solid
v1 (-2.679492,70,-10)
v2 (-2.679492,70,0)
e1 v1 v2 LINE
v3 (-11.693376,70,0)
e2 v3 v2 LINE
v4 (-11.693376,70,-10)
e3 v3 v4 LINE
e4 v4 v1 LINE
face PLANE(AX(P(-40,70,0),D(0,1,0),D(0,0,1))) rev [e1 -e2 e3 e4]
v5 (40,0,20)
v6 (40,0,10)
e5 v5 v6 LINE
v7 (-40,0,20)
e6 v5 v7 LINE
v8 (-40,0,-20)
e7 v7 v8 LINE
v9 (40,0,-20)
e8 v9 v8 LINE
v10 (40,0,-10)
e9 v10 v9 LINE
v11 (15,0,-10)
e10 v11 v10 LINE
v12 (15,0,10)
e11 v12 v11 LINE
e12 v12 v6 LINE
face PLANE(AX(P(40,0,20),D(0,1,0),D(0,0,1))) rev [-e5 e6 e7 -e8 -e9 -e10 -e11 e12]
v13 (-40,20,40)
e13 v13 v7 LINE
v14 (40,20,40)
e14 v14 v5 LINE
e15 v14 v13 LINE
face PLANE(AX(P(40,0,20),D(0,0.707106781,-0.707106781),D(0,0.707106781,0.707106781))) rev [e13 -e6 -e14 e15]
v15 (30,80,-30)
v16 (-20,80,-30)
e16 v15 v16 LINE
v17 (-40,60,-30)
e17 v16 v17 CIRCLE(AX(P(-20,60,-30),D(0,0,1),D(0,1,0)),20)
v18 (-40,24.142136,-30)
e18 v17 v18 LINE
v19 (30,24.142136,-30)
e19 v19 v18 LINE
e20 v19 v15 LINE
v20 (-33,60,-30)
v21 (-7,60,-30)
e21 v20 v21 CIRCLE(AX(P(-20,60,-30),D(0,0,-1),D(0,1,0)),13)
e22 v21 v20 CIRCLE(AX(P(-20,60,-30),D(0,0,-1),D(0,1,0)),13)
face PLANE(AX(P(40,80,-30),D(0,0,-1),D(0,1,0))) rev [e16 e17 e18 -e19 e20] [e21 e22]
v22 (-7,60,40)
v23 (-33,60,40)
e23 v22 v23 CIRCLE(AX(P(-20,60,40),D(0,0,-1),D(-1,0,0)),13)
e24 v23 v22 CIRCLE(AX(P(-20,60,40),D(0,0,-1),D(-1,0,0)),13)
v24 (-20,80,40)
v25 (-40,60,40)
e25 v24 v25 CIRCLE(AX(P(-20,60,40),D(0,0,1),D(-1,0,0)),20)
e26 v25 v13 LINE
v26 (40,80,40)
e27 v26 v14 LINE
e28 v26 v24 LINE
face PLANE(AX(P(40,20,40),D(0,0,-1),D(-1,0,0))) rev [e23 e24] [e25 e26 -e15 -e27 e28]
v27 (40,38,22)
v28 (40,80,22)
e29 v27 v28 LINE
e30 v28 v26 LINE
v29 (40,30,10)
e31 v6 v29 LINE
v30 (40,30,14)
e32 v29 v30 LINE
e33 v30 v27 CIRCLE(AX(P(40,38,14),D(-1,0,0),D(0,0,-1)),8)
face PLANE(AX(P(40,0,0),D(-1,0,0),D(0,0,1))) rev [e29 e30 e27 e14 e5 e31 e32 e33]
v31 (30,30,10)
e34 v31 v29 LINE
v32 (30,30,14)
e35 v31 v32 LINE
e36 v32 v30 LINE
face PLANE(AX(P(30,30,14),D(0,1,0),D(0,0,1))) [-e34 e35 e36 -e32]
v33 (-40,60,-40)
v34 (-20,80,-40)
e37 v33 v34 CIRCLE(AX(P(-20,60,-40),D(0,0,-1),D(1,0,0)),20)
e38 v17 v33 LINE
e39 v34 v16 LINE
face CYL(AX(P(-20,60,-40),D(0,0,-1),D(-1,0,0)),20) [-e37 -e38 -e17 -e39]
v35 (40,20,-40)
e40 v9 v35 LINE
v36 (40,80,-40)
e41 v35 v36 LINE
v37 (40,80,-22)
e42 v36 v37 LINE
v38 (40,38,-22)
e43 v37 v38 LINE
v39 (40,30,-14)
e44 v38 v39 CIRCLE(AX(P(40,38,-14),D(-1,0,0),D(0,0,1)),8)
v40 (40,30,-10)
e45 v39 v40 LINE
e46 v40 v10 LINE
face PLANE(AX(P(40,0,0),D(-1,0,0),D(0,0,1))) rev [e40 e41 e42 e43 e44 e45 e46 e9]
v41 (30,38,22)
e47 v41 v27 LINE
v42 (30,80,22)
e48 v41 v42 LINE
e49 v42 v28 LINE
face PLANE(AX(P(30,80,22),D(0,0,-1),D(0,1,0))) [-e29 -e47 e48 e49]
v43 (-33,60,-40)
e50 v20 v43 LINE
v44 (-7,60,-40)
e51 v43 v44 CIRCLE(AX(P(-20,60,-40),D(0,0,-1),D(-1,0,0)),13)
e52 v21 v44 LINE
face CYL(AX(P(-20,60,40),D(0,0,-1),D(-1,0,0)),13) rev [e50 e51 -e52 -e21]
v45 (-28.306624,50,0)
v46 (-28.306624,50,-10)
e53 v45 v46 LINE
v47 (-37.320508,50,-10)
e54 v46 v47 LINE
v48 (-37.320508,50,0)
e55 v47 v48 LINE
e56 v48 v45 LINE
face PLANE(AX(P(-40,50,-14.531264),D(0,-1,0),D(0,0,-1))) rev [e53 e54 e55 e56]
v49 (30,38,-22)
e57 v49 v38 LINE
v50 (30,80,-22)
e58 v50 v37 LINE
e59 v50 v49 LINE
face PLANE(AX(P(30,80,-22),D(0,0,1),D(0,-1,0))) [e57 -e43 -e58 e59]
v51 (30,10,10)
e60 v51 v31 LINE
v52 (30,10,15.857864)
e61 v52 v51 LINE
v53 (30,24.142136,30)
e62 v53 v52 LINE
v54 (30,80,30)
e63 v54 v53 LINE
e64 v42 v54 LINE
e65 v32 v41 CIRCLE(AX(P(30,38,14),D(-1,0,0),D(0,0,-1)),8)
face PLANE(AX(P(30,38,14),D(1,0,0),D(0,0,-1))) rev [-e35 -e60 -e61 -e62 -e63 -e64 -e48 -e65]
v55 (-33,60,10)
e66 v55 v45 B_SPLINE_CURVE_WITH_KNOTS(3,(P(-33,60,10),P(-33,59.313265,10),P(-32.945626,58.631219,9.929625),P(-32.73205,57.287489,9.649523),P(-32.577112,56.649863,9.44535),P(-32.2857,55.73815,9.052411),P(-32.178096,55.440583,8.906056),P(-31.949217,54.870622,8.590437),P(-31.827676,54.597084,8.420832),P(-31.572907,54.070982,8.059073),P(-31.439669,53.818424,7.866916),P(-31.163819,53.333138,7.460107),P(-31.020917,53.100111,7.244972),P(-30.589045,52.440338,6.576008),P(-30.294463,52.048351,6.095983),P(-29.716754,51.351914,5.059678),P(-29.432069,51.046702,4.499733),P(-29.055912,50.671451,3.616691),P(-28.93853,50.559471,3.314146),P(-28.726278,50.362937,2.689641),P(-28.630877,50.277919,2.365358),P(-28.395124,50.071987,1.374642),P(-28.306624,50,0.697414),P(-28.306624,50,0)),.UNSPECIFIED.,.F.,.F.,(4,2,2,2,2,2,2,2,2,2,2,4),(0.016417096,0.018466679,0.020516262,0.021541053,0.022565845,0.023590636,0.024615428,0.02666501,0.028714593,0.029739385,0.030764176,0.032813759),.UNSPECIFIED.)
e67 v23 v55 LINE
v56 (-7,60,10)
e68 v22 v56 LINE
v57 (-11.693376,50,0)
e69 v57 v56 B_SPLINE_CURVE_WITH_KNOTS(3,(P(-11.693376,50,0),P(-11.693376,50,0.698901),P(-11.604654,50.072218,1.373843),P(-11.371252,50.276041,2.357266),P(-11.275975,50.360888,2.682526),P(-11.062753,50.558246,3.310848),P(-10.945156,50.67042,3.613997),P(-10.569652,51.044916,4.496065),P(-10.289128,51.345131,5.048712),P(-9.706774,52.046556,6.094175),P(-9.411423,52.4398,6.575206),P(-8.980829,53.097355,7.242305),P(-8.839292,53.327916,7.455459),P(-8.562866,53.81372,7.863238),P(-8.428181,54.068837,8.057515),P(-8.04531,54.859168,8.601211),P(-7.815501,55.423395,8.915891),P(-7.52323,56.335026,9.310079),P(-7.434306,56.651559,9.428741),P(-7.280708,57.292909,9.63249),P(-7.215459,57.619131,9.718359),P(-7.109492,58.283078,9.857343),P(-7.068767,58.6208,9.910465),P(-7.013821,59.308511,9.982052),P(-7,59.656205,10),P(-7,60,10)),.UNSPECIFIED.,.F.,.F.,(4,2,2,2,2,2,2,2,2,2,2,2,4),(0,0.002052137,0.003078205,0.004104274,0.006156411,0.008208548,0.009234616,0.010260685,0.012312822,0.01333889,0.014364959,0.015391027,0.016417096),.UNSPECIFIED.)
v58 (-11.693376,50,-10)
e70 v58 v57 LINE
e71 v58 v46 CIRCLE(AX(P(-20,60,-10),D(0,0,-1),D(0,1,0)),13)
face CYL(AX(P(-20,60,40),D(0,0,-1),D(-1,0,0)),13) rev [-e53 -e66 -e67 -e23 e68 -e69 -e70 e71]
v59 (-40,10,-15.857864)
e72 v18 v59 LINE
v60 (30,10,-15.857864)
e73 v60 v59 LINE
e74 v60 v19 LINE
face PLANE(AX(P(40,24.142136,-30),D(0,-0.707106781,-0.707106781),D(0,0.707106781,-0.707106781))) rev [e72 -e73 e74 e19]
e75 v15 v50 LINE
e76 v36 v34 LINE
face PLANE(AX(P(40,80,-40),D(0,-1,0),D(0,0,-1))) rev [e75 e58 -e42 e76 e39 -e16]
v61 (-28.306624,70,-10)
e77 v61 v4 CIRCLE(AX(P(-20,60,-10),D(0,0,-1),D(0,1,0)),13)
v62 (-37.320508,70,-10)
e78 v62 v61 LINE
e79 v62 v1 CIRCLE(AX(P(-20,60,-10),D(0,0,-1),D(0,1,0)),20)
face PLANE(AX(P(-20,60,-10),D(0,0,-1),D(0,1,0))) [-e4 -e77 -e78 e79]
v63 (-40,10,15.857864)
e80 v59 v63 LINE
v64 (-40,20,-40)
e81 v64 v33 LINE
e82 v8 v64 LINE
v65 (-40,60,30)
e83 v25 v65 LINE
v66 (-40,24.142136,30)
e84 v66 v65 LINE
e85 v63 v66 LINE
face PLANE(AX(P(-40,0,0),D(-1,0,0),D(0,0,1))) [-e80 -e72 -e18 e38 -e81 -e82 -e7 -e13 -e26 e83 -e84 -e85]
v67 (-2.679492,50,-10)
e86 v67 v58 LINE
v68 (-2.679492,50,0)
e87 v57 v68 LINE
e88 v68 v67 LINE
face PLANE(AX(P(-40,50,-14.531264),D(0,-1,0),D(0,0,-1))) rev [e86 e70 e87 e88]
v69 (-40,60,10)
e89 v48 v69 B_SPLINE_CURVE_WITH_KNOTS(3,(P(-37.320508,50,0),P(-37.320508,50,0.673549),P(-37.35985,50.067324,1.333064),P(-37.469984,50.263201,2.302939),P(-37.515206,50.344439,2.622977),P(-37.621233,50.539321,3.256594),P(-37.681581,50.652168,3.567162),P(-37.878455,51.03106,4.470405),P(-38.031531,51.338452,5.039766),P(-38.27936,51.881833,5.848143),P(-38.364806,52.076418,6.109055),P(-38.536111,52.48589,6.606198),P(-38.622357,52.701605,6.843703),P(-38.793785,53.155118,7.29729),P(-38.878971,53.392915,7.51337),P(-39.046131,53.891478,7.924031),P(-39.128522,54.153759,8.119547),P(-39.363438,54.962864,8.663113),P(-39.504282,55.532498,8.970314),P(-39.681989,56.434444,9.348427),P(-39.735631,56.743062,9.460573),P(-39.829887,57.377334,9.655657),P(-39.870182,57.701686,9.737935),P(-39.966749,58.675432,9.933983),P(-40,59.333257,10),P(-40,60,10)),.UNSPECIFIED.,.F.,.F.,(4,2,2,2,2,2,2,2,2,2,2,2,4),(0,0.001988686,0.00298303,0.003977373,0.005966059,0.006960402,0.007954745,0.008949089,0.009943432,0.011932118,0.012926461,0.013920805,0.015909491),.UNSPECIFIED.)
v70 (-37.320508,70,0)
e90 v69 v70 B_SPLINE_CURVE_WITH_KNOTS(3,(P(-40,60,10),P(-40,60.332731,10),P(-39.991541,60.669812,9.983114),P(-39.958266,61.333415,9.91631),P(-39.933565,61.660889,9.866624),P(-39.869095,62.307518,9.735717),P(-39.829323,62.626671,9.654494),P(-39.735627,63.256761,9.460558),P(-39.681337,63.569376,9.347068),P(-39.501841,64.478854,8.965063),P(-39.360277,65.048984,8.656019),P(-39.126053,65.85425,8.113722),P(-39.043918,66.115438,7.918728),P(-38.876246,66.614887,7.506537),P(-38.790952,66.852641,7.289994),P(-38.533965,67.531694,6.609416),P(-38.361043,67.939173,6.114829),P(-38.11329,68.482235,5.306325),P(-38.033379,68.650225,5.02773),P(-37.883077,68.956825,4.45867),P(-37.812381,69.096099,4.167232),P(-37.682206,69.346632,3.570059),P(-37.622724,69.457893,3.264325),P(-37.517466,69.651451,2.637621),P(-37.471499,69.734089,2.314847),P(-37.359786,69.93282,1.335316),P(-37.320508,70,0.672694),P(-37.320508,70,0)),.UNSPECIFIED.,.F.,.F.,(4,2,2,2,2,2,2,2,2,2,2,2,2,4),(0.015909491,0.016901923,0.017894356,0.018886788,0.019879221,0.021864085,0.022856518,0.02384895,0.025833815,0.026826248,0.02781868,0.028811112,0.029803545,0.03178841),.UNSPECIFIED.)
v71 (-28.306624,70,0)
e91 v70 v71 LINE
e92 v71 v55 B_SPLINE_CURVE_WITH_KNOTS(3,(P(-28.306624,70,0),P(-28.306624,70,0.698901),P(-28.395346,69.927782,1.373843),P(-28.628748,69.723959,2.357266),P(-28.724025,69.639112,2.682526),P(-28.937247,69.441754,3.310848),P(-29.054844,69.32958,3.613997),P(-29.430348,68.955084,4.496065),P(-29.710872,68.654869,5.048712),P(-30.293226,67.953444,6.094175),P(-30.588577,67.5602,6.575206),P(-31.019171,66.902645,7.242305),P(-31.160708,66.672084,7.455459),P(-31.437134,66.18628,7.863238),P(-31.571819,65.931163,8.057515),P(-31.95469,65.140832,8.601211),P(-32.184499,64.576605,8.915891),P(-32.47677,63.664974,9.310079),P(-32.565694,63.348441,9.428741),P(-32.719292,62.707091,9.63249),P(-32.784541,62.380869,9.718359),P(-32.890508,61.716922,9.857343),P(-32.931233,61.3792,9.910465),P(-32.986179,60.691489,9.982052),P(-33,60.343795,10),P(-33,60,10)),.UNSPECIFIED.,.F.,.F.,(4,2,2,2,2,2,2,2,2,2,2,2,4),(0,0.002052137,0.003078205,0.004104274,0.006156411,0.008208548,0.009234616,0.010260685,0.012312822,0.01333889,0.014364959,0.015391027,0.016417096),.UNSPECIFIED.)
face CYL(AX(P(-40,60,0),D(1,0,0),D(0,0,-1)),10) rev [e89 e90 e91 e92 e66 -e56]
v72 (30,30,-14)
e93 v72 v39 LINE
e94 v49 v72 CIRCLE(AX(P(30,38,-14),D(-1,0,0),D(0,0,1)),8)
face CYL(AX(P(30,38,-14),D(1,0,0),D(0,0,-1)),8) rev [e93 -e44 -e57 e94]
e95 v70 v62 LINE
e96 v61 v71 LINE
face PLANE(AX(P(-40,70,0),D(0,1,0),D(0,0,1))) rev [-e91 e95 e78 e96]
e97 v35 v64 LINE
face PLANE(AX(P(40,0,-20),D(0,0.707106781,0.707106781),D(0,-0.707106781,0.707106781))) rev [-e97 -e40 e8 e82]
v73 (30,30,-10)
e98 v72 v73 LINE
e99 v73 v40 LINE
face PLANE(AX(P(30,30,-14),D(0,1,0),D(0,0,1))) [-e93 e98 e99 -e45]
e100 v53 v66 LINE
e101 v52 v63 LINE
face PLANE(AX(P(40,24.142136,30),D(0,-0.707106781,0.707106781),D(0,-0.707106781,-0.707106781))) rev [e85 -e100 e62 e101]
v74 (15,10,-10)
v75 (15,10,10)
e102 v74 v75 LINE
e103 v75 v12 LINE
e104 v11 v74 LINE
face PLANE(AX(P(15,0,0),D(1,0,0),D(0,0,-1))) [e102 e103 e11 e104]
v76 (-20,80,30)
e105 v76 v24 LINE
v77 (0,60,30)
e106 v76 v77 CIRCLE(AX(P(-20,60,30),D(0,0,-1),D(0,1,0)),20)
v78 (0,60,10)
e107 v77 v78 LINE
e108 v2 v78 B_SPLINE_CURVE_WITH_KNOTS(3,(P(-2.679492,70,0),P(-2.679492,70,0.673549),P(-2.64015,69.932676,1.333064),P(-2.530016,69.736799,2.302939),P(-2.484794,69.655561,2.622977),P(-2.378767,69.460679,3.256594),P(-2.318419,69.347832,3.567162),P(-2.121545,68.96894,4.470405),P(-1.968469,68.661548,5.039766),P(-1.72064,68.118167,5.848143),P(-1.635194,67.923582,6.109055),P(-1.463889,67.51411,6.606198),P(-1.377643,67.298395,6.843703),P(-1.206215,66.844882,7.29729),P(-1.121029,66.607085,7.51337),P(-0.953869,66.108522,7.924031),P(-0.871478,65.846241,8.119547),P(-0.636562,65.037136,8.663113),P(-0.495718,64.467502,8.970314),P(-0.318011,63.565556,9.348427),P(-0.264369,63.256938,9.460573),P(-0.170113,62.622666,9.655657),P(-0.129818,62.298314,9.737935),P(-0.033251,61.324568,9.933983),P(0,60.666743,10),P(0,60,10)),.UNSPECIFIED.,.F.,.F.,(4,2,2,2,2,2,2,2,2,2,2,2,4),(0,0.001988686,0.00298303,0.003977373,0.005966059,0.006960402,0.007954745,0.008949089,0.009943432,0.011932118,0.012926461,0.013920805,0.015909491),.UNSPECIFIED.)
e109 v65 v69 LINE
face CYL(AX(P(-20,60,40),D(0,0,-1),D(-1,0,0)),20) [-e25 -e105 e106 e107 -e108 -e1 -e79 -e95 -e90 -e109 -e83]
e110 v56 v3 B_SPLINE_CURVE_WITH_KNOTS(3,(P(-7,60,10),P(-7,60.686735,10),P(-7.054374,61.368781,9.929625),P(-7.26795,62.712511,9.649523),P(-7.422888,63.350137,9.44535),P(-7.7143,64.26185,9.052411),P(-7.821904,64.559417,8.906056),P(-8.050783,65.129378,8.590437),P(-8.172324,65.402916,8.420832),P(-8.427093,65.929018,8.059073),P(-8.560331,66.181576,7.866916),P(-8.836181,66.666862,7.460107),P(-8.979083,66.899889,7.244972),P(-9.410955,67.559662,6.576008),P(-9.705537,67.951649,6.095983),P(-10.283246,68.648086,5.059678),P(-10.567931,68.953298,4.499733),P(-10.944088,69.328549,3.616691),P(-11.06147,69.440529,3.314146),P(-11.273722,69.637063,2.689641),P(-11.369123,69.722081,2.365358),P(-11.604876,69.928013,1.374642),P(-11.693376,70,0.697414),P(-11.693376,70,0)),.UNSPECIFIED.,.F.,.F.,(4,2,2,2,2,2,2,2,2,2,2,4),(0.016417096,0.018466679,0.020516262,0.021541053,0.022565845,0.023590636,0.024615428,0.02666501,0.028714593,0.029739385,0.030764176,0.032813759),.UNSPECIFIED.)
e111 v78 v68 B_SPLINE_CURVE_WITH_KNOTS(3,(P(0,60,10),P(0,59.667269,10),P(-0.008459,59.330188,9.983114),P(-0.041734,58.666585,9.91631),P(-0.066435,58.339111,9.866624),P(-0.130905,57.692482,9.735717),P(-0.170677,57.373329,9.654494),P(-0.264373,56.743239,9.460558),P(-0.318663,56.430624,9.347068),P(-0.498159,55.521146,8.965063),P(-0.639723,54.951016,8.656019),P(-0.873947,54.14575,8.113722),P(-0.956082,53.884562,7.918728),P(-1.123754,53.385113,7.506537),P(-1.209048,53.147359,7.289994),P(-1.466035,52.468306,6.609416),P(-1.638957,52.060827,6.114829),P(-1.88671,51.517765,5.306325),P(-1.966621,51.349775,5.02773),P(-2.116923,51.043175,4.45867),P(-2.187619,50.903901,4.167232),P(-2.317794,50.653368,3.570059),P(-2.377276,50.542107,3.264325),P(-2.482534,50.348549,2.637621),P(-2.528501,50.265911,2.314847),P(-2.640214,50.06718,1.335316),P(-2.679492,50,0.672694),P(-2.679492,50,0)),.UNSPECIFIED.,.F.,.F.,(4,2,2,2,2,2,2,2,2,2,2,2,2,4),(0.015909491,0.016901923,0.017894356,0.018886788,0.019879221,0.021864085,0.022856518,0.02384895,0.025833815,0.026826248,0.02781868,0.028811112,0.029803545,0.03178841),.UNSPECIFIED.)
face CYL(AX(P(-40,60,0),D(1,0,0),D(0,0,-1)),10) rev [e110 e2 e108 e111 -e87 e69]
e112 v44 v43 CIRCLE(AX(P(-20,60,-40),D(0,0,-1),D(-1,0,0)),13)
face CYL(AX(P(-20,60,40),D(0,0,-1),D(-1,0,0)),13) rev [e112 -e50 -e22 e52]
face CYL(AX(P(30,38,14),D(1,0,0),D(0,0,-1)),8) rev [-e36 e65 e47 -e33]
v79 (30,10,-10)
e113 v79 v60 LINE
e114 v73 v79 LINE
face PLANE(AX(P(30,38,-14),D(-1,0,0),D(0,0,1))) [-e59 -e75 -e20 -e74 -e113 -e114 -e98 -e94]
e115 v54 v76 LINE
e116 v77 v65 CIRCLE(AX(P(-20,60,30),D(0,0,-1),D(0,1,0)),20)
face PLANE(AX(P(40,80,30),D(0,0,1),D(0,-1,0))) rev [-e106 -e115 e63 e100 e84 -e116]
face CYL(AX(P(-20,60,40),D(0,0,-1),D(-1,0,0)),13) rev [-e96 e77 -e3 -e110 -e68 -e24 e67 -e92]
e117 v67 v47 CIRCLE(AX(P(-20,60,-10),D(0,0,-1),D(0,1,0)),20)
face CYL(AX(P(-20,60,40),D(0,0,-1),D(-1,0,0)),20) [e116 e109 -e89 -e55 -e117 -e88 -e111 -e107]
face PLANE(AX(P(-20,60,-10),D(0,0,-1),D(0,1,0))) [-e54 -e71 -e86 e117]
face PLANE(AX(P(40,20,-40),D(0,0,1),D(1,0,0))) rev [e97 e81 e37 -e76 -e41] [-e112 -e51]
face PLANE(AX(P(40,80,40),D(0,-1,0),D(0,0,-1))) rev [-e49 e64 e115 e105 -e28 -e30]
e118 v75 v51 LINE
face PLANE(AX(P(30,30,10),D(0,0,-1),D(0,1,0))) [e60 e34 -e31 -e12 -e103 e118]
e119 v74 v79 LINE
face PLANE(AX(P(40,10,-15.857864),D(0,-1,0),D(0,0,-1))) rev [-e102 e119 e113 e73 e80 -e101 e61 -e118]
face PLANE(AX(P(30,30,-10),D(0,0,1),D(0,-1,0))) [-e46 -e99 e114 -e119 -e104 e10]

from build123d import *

# Parameters (mm, degrees)
SADDLE_BODY_DEPTH     = 40
ARM_TOP_ROUNDS_R20_R  = 20
SIDE_BOSS_DEPTH       = 10
BOSS_POCKET_SKETCH_W  = 20
BOSS_POCKET_SKETCH_H  = 10
BOSS_POCKET_CUT_DEPTH = 25
JOURNAL_BOSS_SKETCH_R = 20
JOURNAL_BOSS_DEPTH    = 40
BASE_SLOT_20X60_DEPTH = 98.979589711
JOURNAL_BORE_SKETCH_R = 13
JOURNAL_BORE_26_DEPTH = 121.0000001


with BuildPart() as part:
    # Saddle Profile Sketch → Saddle Body (new, symmetric)
    with BuildSketch(Plane(origin=(0, 0, 0), x_dir=(0, 0, -1), z_dir=(1, 0, 0))):
        Polygon((-20, 0), (20, 0), (40, 20), (40, 80), (30, 80), (30, 24.142135624), (15.857864376, 10), (-15.857864376, 10), (-30, 24.142135624), (-30, 80), (-40, 80), (-40, 20), align=None)
    extrude(amount=SADDLE_BODY_DEPTH, both=True)

    # Arm Top Rounds R20
    arm_top_rounds_r20_edges = [part.edges().sort_by_distance(p)[0] for p in [
        (-40, 80, 35),
        (-40, 80, -35),
    ]]
    fillet(arm_top_rounds_r20_edges, radius=ARM_TOP_ROUNDS_R20_R)

    # Side Boss Sketch → Side Boss (add)
    with BuildSketch(Plane(origin=(40, 0, 0), x_dir=(0, 0, -1), z_dir=(1, 0, 0))):
        with BuildLine():
            Line((-30, 80), (-22, 80))
            Line((-22, 80), (-22, 38))
            ThreePointArc((-22, 38), (-19.656854249, 32.343145751), (-14, 30))
            Line((-14, 30), (-10, 30))
            Line((-10, 30), (-10, 10))
            Line((-10, 10), (-15.857864376, 10))
            Line((-15.857864376, 10), (-30, 24.142135624))
            Line((-30, 24.142135624), (-30, 80))
        make_face()
        with BuildLine():
            Line((10, 30), (10, 10))
            Line((10, 10), (15.857864376, 10))
            Line((15.857864376, 10), (30, 24.142135624))
            Line((30, 24.142135624), (30, 80))
            Line((30, 80), (22, 80))
            Line((22, 80), (22, 38))
            ThreePointArc((22, 38), (19.656854249, 32.343145751), (14, 30))
            Line((14, 30), (10, 30))
        make_face()
    extrude(amount=-SIDE_BOSS_DEPTH)

    # Boss Pocket Sketch → Boss Pocket Cut (cut)
    with BuildSketch(Plane(origin=(40, 0, 0), x_dir=(0, 0, -1), z_dir=(1, 0, 0))):
        with Locations((0, 5)):
            Rectangle(BOSS_POCKET_SKETCH_W, BOSS_POCKET_SKETCH_H)
    extrude(amount=-BOSS_POCKET_CUT_DEPTH, mode=Mode.SUBTRACT)

    # Journal Boss Sketch → Journal Boss (add)
    with BuildSketch(Plane(origin=(0, 0, 30), x_dir=(-1, 0, 0), z_dir=(0, 0, -1))):
        with Locations(Location((20, 60, 0), (0, 0, 90))):
            Circle(JOURNAL_BOSS_SKETCH_R)
    extrude(amount=JOURNAL_BOSS_DEPTH)

    # Base Slot Sketch → Base Slot 20x60 (cut, through all)
    with BuildSketch(Plane(origin=(0, 0, 0), x_dir=(0, 0, -1), z_dir=(1, 0, 0))):
        with BuildLine():
            Line((0, 70), (14.531264235, 70))
            Line((14.531264235, 70), (14.531264235, 50))
            Line((14.531264235, 50), (0, 50))
            ThreePointArc((0, 50), (-10, 60), (0, 70))
        make_face()
    extrude(amount=-BASE_SLOT_20X60_DEPTH, mode=Mode.SUBTRACT)

    # Journal Bore Sketch → Journal Bore Ø26 (cut, through all)
    with BuildSketch(Plane(origin=(0, 0, -40), x_dir=(-1, 0, 0), z_dir=(0, 0, -1))):
        with Locations((20, 60)):
            Circle(JOURNAL_BORE_SKETCH_R)
    extrude(amount=-JOURNAL_BORE_26_DEPTH, mode=Mode.SUBTRACT)


solid = part.part
